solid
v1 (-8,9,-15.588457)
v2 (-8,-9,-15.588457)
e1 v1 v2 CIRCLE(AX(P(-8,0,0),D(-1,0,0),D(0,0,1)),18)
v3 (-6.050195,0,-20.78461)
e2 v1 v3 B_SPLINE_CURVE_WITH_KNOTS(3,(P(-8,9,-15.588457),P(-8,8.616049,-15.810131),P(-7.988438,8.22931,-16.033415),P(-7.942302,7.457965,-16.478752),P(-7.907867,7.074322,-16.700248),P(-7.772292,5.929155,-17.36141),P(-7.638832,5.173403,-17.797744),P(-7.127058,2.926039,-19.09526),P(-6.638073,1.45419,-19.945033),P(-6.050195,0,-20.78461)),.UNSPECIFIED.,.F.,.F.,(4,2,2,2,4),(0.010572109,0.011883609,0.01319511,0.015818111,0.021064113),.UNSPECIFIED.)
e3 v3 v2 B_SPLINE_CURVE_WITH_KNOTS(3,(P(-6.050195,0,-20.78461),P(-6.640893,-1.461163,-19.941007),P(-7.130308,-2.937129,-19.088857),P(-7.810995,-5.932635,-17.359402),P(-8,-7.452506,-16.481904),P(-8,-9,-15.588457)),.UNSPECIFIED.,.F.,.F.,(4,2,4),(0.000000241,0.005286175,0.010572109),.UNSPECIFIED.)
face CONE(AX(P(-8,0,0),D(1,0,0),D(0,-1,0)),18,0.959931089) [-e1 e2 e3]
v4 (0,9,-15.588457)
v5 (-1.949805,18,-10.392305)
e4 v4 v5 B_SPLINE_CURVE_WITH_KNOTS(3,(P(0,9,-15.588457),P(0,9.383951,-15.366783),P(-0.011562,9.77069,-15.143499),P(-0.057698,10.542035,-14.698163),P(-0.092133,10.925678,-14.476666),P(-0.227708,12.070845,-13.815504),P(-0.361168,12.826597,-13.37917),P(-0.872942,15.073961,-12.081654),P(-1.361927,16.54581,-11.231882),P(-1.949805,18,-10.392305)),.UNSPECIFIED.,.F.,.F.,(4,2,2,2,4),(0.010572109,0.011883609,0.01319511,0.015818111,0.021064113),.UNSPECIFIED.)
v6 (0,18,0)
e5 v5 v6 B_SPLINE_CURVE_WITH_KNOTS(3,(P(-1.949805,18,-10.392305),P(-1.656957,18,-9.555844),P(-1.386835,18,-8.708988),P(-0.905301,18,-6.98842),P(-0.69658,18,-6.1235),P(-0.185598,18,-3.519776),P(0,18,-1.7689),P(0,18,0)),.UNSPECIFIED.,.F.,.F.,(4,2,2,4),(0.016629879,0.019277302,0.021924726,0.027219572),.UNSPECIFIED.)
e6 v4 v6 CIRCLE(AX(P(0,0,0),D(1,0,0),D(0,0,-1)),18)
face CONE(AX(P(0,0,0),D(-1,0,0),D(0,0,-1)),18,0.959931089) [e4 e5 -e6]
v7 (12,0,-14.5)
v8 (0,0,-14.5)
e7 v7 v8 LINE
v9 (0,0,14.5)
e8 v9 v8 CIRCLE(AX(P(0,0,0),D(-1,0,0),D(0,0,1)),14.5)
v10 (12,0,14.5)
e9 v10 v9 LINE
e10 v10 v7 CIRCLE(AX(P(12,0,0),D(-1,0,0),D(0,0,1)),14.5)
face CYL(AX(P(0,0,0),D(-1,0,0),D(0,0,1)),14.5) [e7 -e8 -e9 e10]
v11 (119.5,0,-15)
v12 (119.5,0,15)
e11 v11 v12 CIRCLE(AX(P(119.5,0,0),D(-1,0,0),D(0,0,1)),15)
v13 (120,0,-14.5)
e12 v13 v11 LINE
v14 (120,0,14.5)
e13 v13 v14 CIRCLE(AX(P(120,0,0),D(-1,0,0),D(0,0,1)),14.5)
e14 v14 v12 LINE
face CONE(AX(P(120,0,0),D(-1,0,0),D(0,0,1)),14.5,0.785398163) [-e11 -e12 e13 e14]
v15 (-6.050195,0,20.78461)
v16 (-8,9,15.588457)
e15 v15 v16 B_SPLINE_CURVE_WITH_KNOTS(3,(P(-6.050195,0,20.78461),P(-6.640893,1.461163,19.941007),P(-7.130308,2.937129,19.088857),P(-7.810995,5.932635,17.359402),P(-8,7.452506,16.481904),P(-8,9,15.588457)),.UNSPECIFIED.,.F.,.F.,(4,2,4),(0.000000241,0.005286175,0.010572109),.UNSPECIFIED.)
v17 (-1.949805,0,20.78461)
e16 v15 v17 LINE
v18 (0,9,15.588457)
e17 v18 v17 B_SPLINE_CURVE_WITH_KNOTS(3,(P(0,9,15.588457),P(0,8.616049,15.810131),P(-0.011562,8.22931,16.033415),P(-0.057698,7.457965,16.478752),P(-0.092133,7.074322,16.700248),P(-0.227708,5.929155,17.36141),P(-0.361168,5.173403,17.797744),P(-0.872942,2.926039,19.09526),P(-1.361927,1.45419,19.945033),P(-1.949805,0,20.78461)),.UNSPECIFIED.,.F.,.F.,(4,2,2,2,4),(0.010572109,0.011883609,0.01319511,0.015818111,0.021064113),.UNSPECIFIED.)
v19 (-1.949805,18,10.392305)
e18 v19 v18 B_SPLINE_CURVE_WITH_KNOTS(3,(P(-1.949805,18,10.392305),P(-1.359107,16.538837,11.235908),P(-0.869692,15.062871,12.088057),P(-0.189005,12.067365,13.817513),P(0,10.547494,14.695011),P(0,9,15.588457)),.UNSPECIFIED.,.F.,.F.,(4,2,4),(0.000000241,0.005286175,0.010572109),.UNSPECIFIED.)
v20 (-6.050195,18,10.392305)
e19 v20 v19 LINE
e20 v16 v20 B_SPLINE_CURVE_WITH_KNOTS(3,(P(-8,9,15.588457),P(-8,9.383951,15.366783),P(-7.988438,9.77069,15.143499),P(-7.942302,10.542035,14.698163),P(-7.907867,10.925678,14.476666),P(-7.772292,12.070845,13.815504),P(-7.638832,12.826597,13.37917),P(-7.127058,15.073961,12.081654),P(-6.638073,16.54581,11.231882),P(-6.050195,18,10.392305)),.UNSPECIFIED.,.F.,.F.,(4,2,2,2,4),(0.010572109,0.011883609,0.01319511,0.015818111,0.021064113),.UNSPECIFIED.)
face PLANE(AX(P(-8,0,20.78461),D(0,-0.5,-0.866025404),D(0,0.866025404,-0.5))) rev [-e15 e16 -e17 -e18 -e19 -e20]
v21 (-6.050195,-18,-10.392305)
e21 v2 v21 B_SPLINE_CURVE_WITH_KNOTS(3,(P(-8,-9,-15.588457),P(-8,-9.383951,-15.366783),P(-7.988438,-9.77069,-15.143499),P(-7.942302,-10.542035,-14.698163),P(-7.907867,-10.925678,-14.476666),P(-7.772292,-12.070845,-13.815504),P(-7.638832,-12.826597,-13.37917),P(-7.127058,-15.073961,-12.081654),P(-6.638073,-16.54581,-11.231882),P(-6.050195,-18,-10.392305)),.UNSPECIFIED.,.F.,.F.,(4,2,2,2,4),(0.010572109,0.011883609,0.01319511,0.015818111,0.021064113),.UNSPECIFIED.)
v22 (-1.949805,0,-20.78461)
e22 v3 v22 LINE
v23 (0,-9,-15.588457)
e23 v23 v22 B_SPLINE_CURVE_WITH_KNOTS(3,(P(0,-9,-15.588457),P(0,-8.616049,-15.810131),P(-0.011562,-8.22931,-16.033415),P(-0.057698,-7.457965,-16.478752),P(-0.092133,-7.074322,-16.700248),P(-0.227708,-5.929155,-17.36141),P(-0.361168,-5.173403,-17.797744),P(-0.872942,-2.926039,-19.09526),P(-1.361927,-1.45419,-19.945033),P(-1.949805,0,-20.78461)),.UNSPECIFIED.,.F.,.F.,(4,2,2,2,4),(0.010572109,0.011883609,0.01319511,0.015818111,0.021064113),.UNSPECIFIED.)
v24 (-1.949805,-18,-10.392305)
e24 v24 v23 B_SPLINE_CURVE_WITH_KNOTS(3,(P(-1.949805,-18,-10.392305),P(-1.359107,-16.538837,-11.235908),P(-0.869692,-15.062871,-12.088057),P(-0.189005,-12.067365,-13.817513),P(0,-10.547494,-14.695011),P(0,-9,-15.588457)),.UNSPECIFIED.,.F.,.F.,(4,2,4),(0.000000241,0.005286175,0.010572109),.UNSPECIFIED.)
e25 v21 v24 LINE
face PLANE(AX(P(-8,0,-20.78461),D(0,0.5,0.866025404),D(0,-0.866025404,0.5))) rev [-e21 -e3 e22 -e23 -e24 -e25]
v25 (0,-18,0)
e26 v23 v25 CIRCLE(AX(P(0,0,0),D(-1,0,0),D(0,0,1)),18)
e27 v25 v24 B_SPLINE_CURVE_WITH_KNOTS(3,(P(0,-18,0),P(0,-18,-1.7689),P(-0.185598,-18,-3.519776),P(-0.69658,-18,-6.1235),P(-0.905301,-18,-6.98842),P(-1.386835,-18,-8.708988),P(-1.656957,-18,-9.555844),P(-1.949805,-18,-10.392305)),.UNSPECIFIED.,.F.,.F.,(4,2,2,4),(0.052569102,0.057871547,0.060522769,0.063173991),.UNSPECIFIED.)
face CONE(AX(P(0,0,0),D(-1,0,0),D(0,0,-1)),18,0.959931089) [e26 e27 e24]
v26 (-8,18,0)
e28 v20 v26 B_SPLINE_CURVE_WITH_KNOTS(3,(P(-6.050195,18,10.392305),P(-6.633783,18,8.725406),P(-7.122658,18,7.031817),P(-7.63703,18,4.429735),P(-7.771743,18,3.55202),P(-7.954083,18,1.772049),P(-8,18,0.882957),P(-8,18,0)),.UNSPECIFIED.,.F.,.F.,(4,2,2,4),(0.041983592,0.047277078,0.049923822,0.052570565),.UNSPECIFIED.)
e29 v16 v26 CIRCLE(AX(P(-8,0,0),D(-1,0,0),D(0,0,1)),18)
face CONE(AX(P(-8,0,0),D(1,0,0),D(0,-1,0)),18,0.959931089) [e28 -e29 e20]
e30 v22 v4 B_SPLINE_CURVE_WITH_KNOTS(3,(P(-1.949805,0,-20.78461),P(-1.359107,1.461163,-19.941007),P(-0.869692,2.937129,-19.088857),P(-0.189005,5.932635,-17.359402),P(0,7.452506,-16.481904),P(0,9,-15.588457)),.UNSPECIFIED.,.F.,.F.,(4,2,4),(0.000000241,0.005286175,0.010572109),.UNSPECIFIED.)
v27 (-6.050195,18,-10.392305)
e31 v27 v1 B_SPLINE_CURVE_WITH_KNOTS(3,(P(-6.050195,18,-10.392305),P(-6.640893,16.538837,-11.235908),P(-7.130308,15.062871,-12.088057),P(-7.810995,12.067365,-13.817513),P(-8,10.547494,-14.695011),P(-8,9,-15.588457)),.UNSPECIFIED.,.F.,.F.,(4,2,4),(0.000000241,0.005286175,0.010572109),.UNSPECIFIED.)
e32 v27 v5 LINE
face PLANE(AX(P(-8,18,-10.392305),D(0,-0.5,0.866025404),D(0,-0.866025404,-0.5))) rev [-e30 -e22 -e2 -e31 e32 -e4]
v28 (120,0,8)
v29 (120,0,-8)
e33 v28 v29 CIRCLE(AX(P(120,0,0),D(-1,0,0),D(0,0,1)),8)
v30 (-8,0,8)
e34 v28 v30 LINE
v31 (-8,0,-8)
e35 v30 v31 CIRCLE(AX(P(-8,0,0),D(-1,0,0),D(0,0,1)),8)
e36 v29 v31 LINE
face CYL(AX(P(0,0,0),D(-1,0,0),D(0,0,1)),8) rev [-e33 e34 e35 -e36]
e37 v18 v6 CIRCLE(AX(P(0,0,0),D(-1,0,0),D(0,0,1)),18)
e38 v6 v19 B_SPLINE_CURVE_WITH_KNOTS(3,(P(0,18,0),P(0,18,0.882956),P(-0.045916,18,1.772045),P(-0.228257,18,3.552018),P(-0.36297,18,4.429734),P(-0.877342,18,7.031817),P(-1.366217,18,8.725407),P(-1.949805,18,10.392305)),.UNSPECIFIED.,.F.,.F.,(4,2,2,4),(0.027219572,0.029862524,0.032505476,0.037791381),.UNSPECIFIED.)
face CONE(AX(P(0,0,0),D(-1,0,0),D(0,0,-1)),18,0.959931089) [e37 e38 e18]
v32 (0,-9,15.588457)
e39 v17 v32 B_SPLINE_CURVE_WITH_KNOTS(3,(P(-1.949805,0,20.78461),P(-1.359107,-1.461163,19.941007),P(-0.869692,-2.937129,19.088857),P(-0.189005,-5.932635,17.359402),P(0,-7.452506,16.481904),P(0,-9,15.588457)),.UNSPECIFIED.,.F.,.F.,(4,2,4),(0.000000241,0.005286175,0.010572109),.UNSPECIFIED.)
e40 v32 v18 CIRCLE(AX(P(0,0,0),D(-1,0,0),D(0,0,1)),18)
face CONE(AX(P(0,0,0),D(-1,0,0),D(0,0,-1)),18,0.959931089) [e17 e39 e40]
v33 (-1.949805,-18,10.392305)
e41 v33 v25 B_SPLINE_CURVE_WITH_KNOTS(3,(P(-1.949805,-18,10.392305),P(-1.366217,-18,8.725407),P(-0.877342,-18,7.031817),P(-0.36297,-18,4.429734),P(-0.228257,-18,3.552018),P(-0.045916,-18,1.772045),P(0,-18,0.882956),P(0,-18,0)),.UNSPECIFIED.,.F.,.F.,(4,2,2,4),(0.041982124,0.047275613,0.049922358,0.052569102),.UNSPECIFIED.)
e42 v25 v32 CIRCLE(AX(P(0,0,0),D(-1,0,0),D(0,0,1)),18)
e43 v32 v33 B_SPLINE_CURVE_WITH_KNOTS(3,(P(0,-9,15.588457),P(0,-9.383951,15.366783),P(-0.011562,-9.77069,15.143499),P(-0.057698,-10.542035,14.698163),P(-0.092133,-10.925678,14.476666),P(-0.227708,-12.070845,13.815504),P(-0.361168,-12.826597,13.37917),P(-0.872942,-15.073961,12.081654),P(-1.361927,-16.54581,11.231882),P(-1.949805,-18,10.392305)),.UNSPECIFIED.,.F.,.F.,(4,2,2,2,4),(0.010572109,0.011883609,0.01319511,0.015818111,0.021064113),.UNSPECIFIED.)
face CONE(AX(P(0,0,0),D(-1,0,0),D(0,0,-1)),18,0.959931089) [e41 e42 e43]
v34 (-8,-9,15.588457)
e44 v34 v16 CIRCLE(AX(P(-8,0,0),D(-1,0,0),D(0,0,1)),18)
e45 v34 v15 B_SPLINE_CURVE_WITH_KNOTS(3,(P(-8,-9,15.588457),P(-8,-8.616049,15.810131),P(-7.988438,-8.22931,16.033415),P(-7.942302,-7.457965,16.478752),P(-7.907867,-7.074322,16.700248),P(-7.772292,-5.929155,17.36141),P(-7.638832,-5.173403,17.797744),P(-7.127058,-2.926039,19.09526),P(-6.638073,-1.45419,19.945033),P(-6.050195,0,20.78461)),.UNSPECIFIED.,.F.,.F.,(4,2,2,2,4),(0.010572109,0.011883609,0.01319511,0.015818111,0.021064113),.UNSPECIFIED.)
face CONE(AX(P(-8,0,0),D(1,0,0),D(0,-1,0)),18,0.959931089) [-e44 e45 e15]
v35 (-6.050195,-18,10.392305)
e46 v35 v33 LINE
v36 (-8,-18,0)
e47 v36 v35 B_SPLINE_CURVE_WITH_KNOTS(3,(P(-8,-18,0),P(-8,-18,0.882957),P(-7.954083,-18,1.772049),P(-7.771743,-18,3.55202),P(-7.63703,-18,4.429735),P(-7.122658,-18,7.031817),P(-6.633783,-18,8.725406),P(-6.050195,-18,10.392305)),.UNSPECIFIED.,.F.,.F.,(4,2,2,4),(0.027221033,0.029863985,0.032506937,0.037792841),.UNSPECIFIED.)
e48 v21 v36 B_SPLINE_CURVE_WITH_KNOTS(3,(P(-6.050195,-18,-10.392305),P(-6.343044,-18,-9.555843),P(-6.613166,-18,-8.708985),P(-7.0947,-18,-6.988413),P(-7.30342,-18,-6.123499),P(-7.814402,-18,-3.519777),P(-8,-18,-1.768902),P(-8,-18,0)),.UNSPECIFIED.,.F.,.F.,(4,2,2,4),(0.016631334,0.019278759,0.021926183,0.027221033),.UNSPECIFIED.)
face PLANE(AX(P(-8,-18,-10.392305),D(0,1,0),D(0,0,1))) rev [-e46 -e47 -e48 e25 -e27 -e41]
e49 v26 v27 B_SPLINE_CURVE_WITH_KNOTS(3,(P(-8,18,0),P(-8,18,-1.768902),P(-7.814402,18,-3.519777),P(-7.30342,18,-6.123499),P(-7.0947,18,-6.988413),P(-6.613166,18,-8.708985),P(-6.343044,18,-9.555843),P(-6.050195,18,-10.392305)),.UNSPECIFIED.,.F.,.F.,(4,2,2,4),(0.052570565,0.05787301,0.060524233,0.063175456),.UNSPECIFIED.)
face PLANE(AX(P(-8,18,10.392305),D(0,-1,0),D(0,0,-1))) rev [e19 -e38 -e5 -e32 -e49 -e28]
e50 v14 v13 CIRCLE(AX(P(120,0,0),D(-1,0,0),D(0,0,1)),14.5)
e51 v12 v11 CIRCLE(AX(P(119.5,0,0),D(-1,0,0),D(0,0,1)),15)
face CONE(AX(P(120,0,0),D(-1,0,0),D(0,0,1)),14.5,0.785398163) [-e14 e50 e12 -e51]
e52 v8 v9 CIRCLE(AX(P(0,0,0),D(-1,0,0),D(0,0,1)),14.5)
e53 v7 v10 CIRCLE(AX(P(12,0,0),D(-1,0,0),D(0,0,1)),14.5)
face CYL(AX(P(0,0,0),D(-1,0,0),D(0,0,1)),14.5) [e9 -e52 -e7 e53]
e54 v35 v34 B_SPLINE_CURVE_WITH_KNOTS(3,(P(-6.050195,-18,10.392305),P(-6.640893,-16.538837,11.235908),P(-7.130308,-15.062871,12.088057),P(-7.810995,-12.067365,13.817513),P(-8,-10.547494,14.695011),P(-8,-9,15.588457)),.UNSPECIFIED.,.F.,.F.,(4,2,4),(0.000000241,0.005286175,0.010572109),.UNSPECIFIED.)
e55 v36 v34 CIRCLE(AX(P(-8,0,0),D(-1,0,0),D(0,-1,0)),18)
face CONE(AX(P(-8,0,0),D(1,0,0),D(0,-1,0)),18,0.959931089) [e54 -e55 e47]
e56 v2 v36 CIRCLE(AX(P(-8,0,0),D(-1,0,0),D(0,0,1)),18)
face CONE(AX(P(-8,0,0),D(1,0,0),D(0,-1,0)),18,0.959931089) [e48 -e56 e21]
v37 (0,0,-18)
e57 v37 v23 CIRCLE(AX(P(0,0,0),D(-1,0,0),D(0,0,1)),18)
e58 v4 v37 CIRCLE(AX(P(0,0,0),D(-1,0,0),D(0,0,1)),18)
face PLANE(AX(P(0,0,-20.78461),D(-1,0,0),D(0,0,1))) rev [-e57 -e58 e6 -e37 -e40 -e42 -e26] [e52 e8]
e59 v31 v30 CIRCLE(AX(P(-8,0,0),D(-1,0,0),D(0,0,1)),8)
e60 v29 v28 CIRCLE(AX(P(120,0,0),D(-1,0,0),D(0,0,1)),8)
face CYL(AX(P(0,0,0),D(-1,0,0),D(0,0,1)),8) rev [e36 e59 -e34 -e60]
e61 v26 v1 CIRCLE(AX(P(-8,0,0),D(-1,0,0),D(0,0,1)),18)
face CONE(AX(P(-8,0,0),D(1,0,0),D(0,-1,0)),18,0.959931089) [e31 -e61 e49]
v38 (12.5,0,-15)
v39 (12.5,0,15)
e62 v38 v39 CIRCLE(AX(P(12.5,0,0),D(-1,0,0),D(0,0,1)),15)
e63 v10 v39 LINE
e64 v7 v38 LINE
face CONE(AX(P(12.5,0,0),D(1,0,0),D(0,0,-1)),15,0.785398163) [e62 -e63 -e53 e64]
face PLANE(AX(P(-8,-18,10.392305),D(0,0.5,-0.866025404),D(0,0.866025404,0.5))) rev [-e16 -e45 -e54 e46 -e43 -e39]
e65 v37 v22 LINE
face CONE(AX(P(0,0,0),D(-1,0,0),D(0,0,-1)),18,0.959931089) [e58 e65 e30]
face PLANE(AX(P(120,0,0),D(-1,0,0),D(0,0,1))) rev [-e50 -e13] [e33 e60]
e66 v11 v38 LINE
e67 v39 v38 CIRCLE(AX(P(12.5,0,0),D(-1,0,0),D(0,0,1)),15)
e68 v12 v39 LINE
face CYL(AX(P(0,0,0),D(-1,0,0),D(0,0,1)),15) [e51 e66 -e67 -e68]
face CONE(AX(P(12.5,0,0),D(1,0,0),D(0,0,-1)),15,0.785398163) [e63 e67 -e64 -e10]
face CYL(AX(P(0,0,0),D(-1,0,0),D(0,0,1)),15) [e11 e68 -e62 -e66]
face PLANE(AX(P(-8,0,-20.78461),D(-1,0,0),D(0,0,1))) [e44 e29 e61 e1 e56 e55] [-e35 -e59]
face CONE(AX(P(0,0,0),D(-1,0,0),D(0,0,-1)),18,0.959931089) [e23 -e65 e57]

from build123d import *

# Parameters (mm, degrees)
EXTRUDE_714_DEPTH      = 8
SKETCH_2_2_R           = 23.58
SKETCH_2_2_R_2         = 18
CUT_EXTRUDE_1047_DEPTH = 8
CUT_EXTRUDE_1047_DRAFT = -55
SKETCH_5_R             = 23.569219382
SKETCH_5_R_2           = 18
CUT_EXTRUDE_2_DEPTH    = 6.0502
CUT_EXTRUDE_2_DRAFT    = -55


with BuildPart() as part:
    # Sketch 2 → 旋转1 (revolve)
    with BuildSketch(Plane.XY, mode=Mode.PRIVATE) as revolve_1_sk:
        Polygon((0, 0), (120, 0), (120, 14.5), (119.5, 15), (12.5, 15), (12, 14.5), (0, 14.5), align=None)
    revolve(revolve_1_sk.sketch.rotate(Axis((0, 0, 0), (1, 0, 0)), 90), axis=Axis((0, 0, 0), (1, 0, 0)))

    # Sketch 1 → Extrude 714 (add)
    with BuildSketch(Plane(origin=(0, -0.910076524, 0.397317176), x_dir=(0, 0, 1), z_dir=(-1, 0, 0))):
        Polygon((-21.181926867, 0.910076524), (-10.789622021, -17.089923476), (9.99498767, -17.089923476), (20.387292515, 0.910076524), (9.99498767, 18.910076524), (-10.789622021, 18.910076524), align=None)
    extrude(amount=EXTRUDE_714_DEPTH)


with BuildPart() as cut_extrude_1047_tool:
    # Sketch 2 2 → Cut-Extrude 1047 (with draft: the straight prism first)
    with BuildSketch(Plane.ZY.offset(8)):
        Circle(SKETCH_2_2_R)
        Circle(SKETCH_2_2_R_2, mode=Mode.SUBTRACT)
    extrude(amount=-CUT_EXTRUDE_1047_DEPTH)
    # Cut-Extrude 1047: the draft: its side faces are tilted about the plane it starts from
    cut_extrude_1047_sides = [cut_extrude_1047_tool.faces().sort_by_distance(p)[0] for p in [
        (-4, 0, -23.58),
        (-4, 0, -18),
    ]]
    draft(cut_extrude_1047_sides, Plane.ZY.offset(8), CUT_EXTRUDE_1047_DRAFT)


with BuildPart() as part_1:
    add(part.part)

    # Cut-Extrude 1047: cut by cut_extrude_1047_tool
    add(cut_extrude_1047_tool.part, mode=Mode.SUBTRACT)


with BuildPart() as cut_extrude_2_tool:
    # 草图5 → 切除-拉伸2 (with draft: the straight prism first)
    with BuildSketch(Plane(origin=(0, 0, 0), x_dir=(0, 0, -1), z_dir=(1, 0, 0))):
        Circle(SKETCH_5_R)
        Circle(SKETCH_5_R_2, mode=Mode.SUBTRACT)
    extrude(amount=-CUT_EXTRUDE_2_DEPTH)
    # 切除-拉伸2: the draft: its side faces are tilted about the plane it starts from
    cut_extrude_2_sides = [cut_extrude_2_tool.faces().sort_by_distance(p)[0] for p in [
        (-3.0251, 0, 23.569219382),
        (-3.0251, 0, 18),
    ]]
    draft(cut_extrude_2_sides, Plane(origin=(0, 0, 0), x_dir=(0, 0, -1), z_dir=(1, 0, 0)), CUT_EXTRUDE_2_DRAFT)


with BuildPart() as part_2:
    add(part_1.part)

    # 切除-拉伸2: cut by cut_extrude_2_tool
    add(cut_extrude_2_tool.part, mode=Mode.SUBTRACT)

    # 草图6 → 切除-旋转1 (revolve, cut)
    with BuildSketch(Plane.XY, mode=Mode.PRIVATE) as cut_revolve_1_sk:
        Polygon((0, 0), (120, 0), (120, 8), (-8, 8), (-8, 0), align=None)
    revolve(cut_revolve_1_sk.sketch.rotate(Axis((0, 0, 0), (1, 0, 0)), 90), axis=Axis((0, 0, 0), (1, 0, 0)), mode=Mode.SUBTRACT)


solid = part_2.part
